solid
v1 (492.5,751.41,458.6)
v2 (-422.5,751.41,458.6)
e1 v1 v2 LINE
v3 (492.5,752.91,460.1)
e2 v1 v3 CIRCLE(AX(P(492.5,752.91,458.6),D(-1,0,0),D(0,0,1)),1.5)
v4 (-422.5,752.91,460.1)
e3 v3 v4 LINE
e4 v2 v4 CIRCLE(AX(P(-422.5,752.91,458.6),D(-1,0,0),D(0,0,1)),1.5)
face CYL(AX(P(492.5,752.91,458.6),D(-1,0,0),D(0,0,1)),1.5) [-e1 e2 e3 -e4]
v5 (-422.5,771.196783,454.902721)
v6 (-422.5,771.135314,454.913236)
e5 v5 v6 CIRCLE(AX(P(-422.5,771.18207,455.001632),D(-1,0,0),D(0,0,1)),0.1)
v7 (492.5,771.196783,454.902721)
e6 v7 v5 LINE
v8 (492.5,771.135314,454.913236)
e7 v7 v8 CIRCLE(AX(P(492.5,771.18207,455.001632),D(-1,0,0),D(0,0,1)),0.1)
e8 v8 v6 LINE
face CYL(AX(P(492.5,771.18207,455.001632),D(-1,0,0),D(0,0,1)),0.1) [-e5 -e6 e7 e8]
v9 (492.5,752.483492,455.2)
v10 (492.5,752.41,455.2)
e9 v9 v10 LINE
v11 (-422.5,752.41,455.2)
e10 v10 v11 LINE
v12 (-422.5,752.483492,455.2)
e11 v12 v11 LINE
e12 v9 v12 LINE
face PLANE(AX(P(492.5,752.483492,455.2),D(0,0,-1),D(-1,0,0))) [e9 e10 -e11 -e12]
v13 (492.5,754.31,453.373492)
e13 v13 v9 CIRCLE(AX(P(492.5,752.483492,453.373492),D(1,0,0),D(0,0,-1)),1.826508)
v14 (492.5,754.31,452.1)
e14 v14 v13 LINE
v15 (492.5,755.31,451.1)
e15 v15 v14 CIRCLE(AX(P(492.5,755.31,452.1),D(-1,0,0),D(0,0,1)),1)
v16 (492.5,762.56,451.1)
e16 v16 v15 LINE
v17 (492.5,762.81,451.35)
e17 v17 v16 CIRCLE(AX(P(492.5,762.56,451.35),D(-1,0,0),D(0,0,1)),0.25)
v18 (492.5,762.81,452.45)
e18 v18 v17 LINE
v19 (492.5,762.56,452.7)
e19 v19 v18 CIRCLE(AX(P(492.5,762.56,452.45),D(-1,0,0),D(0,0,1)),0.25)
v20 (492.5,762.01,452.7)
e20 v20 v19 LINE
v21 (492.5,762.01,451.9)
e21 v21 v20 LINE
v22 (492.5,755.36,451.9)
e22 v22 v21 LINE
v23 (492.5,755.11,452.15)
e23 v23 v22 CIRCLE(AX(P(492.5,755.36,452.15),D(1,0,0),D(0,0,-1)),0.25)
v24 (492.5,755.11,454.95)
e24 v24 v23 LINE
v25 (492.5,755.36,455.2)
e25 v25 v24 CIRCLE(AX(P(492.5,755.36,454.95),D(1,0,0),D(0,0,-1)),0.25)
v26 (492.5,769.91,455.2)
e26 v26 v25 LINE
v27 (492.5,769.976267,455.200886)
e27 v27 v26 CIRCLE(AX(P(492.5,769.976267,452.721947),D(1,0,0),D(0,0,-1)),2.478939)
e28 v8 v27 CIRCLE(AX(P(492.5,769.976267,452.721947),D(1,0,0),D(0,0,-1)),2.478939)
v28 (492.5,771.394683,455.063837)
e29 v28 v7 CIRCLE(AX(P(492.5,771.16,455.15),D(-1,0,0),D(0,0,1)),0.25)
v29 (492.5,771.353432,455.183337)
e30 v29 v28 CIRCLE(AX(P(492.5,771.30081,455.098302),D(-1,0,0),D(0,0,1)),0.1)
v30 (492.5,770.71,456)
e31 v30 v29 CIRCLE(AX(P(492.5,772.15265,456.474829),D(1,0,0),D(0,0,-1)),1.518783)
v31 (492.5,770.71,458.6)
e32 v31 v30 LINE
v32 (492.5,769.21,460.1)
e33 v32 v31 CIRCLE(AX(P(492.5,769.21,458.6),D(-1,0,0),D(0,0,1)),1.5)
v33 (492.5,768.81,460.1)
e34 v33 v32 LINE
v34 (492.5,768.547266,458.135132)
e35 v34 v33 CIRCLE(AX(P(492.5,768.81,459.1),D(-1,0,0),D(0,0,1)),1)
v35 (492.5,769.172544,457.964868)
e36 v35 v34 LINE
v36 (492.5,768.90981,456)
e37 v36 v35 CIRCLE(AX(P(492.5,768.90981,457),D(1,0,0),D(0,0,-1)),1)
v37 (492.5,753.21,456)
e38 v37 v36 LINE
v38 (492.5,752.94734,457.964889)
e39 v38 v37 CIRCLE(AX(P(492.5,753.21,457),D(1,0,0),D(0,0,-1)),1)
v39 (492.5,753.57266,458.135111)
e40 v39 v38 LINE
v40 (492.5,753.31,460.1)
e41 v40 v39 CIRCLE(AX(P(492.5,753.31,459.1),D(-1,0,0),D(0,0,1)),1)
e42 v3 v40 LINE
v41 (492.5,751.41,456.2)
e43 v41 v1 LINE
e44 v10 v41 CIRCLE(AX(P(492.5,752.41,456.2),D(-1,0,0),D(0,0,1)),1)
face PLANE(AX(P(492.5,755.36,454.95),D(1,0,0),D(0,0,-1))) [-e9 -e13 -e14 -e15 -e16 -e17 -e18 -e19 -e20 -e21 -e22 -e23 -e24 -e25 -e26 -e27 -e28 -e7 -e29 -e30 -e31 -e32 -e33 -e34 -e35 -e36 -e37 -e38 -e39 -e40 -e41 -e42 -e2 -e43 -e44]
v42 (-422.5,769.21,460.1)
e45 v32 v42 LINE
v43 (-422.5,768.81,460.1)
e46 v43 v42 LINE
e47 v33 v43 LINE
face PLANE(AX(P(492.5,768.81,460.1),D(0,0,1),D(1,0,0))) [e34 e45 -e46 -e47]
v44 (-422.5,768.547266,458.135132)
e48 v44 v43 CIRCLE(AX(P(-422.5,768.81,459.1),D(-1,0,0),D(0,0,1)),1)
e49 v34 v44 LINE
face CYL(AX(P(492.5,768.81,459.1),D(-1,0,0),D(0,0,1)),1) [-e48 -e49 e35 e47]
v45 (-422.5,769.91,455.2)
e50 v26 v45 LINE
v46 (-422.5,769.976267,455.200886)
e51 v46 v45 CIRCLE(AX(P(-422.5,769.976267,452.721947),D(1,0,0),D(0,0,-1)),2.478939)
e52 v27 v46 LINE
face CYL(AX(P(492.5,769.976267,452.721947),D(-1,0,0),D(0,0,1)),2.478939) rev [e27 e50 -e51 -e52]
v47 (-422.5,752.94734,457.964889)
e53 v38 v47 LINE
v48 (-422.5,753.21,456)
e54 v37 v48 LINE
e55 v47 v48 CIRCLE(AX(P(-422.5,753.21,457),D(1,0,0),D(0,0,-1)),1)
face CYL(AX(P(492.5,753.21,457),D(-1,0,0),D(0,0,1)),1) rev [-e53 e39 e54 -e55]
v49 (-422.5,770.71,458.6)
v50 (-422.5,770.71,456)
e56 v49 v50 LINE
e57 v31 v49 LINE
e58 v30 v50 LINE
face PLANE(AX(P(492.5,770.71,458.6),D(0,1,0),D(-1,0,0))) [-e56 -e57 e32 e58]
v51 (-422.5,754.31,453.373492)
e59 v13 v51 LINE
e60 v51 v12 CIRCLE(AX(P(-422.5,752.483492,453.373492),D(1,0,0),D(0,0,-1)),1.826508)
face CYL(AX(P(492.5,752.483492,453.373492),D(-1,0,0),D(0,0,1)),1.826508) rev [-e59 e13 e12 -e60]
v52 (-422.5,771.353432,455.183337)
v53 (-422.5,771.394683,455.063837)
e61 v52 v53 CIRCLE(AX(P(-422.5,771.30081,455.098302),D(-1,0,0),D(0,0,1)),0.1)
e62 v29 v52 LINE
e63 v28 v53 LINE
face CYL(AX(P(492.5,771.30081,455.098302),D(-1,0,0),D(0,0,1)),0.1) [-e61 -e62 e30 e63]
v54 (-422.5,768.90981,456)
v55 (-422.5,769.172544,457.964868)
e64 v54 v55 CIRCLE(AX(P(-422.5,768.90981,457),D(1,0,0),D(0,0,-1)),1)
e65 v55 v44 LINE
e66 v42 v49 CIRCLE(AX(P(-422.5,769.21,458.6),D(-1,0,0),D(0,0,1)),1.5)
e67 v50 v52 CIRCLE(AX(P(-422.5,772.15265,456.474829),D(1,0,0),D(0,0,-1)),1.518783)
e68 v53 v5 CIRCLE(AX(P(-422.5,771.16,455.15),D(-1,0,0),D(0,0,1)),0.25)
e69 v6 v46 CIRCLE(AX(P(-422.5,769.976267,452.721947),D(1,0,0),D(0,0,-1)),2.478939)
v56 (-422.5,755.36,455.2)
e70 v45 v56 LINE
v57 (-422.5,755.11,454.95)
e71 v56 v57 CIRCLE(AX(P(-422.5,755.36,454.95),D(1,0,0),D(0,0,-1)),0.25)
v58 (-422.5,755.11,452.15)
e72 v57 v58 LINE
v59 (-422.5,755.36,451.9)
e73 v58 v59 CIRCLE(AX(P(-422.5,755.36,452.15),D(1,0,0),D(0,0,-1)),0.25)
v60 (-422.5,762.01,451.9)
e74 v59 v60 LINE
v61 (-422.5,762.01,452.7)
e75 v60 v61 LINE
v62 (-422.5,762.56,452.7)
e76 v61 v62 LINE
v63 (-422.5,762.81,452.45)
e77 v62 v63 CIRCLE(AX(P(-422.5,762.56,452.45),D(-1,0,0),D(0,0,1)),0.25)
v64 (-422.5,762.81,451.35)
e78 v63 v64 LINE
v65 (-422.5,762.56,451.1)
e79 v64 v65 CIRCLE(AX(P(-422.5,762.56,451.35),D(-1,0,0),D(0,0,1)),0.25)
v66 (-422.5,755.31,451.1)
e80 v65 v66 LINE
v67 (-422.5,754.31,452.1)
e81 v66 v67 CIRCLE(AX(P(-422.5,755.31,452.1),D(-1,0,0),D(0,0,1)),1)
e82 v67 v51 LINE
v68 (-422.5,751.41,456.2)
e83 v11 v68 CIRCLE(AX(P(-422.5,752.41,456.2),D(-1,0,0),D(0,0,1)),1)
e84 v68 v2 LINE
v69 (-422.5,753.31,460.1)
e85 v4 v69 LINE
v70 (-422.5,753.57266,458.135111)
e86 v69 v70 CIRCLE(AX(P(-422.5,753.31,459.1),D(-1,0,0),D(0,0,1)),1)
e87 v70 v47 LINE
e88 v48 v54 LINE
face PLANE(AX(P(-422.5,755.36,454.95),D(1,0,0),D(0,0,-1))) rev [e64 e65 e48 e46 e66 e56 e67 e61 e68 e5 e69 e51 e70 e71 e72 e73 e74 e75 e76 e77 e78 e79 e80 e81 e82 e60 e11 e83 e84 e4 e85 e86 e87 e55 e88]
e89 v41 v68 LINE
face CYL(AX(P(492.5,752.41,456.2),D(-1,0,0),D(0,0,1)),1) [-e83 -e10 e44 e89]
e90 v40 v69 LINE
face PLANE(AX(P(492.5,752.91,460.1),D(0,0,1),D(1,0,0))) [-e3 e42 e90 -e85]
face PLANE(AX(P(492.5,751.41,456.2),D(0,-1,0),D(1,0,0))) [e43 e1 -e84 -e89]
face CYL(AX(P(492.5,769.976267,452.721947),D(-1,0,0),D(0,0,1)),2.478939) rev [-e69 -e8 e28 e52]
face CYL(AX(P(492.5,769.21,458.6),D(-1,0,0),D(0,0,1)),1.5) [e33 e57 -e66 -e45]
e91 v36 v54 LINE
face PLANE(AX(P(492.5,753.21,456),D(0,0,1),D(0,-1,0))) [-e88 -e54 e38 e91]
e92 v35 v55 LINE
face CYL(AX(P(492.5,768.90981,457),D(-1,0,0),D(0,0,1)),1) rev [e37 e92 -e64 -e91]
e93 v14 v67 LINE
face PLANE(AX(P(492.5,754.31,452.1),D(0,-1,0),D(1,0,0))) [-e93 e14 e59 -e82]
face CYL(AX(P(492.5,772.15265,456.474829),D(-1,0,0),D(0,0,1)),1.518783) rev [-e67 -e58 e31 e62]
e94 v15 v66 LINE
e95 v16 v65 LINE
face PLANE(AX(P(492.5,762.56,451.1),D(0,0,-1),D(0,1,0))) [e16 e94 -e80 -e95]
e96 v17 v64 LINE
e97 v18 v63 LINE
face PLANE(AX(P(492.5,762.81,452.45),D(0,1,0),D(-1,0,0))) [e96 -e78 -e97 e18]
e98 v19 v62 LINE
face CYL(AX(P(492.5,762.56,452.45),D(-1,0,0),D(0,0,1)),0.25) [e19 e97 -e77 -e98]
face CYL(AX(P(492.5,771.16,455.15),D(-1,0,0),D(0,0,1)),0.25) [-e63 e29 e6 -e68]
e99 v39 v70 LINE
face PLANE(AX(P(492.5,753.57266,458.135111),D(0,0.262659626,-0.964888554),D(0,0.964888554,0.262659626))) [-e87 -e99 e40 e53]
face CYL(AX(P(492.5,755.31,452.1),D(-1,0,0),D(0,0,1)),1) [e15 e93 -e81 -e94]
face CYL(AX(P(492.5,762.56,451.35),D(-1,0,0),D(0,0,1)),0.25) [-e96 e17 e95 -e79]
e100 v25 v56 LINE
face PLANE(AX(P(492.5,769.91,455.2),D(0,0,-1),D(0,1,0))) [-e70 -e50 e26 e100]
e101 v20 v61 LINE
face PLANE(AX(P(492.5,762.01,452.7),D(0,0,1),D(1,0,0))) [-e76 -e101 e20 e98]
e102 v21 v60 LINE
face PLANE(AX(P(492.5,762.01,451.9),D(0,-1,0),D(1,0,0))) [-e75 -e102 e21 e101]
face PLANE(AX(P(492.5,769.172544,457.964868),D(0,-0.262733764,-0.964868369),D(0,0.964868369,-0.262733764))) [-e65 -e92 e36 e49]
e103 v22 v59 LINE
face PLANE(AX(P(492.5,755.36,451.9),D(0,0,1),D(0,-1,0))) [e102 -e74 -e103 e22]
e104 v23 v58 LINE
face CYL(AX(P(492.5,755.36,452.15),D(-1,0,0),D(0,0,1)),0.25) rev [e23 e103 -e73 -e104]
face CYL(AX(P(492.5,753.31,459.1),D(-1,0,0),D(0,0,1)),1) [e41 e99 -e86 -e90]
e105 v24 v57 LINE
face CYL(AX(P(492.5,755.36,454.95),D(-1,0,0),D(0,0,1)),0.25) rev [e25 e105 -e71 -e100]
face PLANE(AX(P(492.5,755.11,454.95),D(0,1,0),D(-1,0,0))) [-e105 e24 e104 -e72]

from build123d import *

# Parameters (mm, degrees)
BOSS_EXTRUDE1_DEPTH = 915


with BuildPart() as part:
    # Sketch1 → Boss-Extrude1 (new body)
    with BuildSketch(Plane(origin=(-422.5, 0, 0), x_dir=(0, -1, 0), z_dir=(-1, 0, 0))):
        with BuildLine():
            Line((-755.11, 454.95), (-755.11, 452.15))
            ThreePointArc((-755.11, 452.15), (-755.183223305, 451.973223305), (-755.36, 451.9))
            Line((-755.36, 451.9), (-762.01, 451.9))
            Line((-762.01, 451.9), (-762.01, 452.7))
            Line((-762.01, 452.7), (-762.56, 452.7))
            ThreePointArc((-762.56, 452.7), (-762.736776695, 452.626776695), (-762.81, 452.45))
            Line((-762.81, 452.45), (-762.81, 451.35))
            ThreePointArc((-762.81, 451.35), (-762.736776695, 451.173223305), (-762.56, 451.1))
            Line((-762.56, 451.1), (-755.31, 451.1))
            ThreePointArc((-755.31, 451.1), (-754.602893219, 451.392893219), (-754.31, 452.1))
            Line((-754.31, 452.1), (-754.31, 453.373491886))
            ThreePointArc((-754.31, 453.373491886), (-753.775028159, 454.665028159), (-752.483491886, 455.2))
            Line((-752.483491886, 455.2), (-752.41, 455.2))
            ThreePointArc((-752.41, 455.2), (-751.702893219, 455.492893219), (-751.41, 456.2))
            Line((-751.41, 456.2), (-751.41, 458.6))
            ThreePointArc((-751.41, 458.6), (-751.849339828, 459.660660172), (-752.91, 460.1))
            Line((-752.91, 460.1), (-753.31, 460.1))
            ThreePointArc((-753.31, 460.1), (-754.301183271, 459.232498012), (-753.572659626, 458.135111446))
            Line((-753.572659626, 458.135111446), (-752.947340374, 457.964888554))
            ThreePointArc((-752.947340374, 457.964888554), (-752.218816729, 456.867501988), (-753.21, 456))
            Line((-753.21, 456), (-768.909810447, 456))
            ThreePointArc((-768.909810447, 456), (-769.900988627, 456.867463908), (-769.172544211, 457.964868369))
            Line((-769.172544211, 457.964868369), (-768.547266236, 458.135131631))
            ThreePointArc((-768.547266236, 458.135131631), (-767.81882182, 459.232536092), (-768.81, 460.1))
            Line((-768.81, 460.1), (-769.21, 460.1))
            ThreePointArc((-769.21, 460.1), (-770.270660172, 459.660660172), (-770.71, 458.6))
            Line((-770.71, 458.6), (-770.71, 456))
            ThreePointArc((-770.71, 456), (-770.959658895, 455.534896264), (-771.353431907, 455.183337075))
            ThreePointArc((-771.353431907, 455.183337075), (-771.39533621, 455.130932577), (-771.394682745, 455.06383731))
            ThreePointArc((-771.394682745, 455.06383731), (-771.317838721, 454.956126495), (-771.196783129, 454.902720811))
            ThreePointArc((-771.196783129, 454.902720811), (-771.165207963, 454.903064362), (-771.135314114, 454.913236231))
            ThreePointArc((-771.135314114, 454.913236231), (-770.541156786, 455.135665686), (-769.91, 455.2))
            Line((-769.91, 455.2), (-755.36, 455.2))
            ThreePointArc((-755.36, 455.2), (-755.183223305, 455.126776695), (-755.11, 454.95))
        make_face()
    extrude(amount=-BOSS_EXTRUDE1_DEPTH)


solid = part.part
